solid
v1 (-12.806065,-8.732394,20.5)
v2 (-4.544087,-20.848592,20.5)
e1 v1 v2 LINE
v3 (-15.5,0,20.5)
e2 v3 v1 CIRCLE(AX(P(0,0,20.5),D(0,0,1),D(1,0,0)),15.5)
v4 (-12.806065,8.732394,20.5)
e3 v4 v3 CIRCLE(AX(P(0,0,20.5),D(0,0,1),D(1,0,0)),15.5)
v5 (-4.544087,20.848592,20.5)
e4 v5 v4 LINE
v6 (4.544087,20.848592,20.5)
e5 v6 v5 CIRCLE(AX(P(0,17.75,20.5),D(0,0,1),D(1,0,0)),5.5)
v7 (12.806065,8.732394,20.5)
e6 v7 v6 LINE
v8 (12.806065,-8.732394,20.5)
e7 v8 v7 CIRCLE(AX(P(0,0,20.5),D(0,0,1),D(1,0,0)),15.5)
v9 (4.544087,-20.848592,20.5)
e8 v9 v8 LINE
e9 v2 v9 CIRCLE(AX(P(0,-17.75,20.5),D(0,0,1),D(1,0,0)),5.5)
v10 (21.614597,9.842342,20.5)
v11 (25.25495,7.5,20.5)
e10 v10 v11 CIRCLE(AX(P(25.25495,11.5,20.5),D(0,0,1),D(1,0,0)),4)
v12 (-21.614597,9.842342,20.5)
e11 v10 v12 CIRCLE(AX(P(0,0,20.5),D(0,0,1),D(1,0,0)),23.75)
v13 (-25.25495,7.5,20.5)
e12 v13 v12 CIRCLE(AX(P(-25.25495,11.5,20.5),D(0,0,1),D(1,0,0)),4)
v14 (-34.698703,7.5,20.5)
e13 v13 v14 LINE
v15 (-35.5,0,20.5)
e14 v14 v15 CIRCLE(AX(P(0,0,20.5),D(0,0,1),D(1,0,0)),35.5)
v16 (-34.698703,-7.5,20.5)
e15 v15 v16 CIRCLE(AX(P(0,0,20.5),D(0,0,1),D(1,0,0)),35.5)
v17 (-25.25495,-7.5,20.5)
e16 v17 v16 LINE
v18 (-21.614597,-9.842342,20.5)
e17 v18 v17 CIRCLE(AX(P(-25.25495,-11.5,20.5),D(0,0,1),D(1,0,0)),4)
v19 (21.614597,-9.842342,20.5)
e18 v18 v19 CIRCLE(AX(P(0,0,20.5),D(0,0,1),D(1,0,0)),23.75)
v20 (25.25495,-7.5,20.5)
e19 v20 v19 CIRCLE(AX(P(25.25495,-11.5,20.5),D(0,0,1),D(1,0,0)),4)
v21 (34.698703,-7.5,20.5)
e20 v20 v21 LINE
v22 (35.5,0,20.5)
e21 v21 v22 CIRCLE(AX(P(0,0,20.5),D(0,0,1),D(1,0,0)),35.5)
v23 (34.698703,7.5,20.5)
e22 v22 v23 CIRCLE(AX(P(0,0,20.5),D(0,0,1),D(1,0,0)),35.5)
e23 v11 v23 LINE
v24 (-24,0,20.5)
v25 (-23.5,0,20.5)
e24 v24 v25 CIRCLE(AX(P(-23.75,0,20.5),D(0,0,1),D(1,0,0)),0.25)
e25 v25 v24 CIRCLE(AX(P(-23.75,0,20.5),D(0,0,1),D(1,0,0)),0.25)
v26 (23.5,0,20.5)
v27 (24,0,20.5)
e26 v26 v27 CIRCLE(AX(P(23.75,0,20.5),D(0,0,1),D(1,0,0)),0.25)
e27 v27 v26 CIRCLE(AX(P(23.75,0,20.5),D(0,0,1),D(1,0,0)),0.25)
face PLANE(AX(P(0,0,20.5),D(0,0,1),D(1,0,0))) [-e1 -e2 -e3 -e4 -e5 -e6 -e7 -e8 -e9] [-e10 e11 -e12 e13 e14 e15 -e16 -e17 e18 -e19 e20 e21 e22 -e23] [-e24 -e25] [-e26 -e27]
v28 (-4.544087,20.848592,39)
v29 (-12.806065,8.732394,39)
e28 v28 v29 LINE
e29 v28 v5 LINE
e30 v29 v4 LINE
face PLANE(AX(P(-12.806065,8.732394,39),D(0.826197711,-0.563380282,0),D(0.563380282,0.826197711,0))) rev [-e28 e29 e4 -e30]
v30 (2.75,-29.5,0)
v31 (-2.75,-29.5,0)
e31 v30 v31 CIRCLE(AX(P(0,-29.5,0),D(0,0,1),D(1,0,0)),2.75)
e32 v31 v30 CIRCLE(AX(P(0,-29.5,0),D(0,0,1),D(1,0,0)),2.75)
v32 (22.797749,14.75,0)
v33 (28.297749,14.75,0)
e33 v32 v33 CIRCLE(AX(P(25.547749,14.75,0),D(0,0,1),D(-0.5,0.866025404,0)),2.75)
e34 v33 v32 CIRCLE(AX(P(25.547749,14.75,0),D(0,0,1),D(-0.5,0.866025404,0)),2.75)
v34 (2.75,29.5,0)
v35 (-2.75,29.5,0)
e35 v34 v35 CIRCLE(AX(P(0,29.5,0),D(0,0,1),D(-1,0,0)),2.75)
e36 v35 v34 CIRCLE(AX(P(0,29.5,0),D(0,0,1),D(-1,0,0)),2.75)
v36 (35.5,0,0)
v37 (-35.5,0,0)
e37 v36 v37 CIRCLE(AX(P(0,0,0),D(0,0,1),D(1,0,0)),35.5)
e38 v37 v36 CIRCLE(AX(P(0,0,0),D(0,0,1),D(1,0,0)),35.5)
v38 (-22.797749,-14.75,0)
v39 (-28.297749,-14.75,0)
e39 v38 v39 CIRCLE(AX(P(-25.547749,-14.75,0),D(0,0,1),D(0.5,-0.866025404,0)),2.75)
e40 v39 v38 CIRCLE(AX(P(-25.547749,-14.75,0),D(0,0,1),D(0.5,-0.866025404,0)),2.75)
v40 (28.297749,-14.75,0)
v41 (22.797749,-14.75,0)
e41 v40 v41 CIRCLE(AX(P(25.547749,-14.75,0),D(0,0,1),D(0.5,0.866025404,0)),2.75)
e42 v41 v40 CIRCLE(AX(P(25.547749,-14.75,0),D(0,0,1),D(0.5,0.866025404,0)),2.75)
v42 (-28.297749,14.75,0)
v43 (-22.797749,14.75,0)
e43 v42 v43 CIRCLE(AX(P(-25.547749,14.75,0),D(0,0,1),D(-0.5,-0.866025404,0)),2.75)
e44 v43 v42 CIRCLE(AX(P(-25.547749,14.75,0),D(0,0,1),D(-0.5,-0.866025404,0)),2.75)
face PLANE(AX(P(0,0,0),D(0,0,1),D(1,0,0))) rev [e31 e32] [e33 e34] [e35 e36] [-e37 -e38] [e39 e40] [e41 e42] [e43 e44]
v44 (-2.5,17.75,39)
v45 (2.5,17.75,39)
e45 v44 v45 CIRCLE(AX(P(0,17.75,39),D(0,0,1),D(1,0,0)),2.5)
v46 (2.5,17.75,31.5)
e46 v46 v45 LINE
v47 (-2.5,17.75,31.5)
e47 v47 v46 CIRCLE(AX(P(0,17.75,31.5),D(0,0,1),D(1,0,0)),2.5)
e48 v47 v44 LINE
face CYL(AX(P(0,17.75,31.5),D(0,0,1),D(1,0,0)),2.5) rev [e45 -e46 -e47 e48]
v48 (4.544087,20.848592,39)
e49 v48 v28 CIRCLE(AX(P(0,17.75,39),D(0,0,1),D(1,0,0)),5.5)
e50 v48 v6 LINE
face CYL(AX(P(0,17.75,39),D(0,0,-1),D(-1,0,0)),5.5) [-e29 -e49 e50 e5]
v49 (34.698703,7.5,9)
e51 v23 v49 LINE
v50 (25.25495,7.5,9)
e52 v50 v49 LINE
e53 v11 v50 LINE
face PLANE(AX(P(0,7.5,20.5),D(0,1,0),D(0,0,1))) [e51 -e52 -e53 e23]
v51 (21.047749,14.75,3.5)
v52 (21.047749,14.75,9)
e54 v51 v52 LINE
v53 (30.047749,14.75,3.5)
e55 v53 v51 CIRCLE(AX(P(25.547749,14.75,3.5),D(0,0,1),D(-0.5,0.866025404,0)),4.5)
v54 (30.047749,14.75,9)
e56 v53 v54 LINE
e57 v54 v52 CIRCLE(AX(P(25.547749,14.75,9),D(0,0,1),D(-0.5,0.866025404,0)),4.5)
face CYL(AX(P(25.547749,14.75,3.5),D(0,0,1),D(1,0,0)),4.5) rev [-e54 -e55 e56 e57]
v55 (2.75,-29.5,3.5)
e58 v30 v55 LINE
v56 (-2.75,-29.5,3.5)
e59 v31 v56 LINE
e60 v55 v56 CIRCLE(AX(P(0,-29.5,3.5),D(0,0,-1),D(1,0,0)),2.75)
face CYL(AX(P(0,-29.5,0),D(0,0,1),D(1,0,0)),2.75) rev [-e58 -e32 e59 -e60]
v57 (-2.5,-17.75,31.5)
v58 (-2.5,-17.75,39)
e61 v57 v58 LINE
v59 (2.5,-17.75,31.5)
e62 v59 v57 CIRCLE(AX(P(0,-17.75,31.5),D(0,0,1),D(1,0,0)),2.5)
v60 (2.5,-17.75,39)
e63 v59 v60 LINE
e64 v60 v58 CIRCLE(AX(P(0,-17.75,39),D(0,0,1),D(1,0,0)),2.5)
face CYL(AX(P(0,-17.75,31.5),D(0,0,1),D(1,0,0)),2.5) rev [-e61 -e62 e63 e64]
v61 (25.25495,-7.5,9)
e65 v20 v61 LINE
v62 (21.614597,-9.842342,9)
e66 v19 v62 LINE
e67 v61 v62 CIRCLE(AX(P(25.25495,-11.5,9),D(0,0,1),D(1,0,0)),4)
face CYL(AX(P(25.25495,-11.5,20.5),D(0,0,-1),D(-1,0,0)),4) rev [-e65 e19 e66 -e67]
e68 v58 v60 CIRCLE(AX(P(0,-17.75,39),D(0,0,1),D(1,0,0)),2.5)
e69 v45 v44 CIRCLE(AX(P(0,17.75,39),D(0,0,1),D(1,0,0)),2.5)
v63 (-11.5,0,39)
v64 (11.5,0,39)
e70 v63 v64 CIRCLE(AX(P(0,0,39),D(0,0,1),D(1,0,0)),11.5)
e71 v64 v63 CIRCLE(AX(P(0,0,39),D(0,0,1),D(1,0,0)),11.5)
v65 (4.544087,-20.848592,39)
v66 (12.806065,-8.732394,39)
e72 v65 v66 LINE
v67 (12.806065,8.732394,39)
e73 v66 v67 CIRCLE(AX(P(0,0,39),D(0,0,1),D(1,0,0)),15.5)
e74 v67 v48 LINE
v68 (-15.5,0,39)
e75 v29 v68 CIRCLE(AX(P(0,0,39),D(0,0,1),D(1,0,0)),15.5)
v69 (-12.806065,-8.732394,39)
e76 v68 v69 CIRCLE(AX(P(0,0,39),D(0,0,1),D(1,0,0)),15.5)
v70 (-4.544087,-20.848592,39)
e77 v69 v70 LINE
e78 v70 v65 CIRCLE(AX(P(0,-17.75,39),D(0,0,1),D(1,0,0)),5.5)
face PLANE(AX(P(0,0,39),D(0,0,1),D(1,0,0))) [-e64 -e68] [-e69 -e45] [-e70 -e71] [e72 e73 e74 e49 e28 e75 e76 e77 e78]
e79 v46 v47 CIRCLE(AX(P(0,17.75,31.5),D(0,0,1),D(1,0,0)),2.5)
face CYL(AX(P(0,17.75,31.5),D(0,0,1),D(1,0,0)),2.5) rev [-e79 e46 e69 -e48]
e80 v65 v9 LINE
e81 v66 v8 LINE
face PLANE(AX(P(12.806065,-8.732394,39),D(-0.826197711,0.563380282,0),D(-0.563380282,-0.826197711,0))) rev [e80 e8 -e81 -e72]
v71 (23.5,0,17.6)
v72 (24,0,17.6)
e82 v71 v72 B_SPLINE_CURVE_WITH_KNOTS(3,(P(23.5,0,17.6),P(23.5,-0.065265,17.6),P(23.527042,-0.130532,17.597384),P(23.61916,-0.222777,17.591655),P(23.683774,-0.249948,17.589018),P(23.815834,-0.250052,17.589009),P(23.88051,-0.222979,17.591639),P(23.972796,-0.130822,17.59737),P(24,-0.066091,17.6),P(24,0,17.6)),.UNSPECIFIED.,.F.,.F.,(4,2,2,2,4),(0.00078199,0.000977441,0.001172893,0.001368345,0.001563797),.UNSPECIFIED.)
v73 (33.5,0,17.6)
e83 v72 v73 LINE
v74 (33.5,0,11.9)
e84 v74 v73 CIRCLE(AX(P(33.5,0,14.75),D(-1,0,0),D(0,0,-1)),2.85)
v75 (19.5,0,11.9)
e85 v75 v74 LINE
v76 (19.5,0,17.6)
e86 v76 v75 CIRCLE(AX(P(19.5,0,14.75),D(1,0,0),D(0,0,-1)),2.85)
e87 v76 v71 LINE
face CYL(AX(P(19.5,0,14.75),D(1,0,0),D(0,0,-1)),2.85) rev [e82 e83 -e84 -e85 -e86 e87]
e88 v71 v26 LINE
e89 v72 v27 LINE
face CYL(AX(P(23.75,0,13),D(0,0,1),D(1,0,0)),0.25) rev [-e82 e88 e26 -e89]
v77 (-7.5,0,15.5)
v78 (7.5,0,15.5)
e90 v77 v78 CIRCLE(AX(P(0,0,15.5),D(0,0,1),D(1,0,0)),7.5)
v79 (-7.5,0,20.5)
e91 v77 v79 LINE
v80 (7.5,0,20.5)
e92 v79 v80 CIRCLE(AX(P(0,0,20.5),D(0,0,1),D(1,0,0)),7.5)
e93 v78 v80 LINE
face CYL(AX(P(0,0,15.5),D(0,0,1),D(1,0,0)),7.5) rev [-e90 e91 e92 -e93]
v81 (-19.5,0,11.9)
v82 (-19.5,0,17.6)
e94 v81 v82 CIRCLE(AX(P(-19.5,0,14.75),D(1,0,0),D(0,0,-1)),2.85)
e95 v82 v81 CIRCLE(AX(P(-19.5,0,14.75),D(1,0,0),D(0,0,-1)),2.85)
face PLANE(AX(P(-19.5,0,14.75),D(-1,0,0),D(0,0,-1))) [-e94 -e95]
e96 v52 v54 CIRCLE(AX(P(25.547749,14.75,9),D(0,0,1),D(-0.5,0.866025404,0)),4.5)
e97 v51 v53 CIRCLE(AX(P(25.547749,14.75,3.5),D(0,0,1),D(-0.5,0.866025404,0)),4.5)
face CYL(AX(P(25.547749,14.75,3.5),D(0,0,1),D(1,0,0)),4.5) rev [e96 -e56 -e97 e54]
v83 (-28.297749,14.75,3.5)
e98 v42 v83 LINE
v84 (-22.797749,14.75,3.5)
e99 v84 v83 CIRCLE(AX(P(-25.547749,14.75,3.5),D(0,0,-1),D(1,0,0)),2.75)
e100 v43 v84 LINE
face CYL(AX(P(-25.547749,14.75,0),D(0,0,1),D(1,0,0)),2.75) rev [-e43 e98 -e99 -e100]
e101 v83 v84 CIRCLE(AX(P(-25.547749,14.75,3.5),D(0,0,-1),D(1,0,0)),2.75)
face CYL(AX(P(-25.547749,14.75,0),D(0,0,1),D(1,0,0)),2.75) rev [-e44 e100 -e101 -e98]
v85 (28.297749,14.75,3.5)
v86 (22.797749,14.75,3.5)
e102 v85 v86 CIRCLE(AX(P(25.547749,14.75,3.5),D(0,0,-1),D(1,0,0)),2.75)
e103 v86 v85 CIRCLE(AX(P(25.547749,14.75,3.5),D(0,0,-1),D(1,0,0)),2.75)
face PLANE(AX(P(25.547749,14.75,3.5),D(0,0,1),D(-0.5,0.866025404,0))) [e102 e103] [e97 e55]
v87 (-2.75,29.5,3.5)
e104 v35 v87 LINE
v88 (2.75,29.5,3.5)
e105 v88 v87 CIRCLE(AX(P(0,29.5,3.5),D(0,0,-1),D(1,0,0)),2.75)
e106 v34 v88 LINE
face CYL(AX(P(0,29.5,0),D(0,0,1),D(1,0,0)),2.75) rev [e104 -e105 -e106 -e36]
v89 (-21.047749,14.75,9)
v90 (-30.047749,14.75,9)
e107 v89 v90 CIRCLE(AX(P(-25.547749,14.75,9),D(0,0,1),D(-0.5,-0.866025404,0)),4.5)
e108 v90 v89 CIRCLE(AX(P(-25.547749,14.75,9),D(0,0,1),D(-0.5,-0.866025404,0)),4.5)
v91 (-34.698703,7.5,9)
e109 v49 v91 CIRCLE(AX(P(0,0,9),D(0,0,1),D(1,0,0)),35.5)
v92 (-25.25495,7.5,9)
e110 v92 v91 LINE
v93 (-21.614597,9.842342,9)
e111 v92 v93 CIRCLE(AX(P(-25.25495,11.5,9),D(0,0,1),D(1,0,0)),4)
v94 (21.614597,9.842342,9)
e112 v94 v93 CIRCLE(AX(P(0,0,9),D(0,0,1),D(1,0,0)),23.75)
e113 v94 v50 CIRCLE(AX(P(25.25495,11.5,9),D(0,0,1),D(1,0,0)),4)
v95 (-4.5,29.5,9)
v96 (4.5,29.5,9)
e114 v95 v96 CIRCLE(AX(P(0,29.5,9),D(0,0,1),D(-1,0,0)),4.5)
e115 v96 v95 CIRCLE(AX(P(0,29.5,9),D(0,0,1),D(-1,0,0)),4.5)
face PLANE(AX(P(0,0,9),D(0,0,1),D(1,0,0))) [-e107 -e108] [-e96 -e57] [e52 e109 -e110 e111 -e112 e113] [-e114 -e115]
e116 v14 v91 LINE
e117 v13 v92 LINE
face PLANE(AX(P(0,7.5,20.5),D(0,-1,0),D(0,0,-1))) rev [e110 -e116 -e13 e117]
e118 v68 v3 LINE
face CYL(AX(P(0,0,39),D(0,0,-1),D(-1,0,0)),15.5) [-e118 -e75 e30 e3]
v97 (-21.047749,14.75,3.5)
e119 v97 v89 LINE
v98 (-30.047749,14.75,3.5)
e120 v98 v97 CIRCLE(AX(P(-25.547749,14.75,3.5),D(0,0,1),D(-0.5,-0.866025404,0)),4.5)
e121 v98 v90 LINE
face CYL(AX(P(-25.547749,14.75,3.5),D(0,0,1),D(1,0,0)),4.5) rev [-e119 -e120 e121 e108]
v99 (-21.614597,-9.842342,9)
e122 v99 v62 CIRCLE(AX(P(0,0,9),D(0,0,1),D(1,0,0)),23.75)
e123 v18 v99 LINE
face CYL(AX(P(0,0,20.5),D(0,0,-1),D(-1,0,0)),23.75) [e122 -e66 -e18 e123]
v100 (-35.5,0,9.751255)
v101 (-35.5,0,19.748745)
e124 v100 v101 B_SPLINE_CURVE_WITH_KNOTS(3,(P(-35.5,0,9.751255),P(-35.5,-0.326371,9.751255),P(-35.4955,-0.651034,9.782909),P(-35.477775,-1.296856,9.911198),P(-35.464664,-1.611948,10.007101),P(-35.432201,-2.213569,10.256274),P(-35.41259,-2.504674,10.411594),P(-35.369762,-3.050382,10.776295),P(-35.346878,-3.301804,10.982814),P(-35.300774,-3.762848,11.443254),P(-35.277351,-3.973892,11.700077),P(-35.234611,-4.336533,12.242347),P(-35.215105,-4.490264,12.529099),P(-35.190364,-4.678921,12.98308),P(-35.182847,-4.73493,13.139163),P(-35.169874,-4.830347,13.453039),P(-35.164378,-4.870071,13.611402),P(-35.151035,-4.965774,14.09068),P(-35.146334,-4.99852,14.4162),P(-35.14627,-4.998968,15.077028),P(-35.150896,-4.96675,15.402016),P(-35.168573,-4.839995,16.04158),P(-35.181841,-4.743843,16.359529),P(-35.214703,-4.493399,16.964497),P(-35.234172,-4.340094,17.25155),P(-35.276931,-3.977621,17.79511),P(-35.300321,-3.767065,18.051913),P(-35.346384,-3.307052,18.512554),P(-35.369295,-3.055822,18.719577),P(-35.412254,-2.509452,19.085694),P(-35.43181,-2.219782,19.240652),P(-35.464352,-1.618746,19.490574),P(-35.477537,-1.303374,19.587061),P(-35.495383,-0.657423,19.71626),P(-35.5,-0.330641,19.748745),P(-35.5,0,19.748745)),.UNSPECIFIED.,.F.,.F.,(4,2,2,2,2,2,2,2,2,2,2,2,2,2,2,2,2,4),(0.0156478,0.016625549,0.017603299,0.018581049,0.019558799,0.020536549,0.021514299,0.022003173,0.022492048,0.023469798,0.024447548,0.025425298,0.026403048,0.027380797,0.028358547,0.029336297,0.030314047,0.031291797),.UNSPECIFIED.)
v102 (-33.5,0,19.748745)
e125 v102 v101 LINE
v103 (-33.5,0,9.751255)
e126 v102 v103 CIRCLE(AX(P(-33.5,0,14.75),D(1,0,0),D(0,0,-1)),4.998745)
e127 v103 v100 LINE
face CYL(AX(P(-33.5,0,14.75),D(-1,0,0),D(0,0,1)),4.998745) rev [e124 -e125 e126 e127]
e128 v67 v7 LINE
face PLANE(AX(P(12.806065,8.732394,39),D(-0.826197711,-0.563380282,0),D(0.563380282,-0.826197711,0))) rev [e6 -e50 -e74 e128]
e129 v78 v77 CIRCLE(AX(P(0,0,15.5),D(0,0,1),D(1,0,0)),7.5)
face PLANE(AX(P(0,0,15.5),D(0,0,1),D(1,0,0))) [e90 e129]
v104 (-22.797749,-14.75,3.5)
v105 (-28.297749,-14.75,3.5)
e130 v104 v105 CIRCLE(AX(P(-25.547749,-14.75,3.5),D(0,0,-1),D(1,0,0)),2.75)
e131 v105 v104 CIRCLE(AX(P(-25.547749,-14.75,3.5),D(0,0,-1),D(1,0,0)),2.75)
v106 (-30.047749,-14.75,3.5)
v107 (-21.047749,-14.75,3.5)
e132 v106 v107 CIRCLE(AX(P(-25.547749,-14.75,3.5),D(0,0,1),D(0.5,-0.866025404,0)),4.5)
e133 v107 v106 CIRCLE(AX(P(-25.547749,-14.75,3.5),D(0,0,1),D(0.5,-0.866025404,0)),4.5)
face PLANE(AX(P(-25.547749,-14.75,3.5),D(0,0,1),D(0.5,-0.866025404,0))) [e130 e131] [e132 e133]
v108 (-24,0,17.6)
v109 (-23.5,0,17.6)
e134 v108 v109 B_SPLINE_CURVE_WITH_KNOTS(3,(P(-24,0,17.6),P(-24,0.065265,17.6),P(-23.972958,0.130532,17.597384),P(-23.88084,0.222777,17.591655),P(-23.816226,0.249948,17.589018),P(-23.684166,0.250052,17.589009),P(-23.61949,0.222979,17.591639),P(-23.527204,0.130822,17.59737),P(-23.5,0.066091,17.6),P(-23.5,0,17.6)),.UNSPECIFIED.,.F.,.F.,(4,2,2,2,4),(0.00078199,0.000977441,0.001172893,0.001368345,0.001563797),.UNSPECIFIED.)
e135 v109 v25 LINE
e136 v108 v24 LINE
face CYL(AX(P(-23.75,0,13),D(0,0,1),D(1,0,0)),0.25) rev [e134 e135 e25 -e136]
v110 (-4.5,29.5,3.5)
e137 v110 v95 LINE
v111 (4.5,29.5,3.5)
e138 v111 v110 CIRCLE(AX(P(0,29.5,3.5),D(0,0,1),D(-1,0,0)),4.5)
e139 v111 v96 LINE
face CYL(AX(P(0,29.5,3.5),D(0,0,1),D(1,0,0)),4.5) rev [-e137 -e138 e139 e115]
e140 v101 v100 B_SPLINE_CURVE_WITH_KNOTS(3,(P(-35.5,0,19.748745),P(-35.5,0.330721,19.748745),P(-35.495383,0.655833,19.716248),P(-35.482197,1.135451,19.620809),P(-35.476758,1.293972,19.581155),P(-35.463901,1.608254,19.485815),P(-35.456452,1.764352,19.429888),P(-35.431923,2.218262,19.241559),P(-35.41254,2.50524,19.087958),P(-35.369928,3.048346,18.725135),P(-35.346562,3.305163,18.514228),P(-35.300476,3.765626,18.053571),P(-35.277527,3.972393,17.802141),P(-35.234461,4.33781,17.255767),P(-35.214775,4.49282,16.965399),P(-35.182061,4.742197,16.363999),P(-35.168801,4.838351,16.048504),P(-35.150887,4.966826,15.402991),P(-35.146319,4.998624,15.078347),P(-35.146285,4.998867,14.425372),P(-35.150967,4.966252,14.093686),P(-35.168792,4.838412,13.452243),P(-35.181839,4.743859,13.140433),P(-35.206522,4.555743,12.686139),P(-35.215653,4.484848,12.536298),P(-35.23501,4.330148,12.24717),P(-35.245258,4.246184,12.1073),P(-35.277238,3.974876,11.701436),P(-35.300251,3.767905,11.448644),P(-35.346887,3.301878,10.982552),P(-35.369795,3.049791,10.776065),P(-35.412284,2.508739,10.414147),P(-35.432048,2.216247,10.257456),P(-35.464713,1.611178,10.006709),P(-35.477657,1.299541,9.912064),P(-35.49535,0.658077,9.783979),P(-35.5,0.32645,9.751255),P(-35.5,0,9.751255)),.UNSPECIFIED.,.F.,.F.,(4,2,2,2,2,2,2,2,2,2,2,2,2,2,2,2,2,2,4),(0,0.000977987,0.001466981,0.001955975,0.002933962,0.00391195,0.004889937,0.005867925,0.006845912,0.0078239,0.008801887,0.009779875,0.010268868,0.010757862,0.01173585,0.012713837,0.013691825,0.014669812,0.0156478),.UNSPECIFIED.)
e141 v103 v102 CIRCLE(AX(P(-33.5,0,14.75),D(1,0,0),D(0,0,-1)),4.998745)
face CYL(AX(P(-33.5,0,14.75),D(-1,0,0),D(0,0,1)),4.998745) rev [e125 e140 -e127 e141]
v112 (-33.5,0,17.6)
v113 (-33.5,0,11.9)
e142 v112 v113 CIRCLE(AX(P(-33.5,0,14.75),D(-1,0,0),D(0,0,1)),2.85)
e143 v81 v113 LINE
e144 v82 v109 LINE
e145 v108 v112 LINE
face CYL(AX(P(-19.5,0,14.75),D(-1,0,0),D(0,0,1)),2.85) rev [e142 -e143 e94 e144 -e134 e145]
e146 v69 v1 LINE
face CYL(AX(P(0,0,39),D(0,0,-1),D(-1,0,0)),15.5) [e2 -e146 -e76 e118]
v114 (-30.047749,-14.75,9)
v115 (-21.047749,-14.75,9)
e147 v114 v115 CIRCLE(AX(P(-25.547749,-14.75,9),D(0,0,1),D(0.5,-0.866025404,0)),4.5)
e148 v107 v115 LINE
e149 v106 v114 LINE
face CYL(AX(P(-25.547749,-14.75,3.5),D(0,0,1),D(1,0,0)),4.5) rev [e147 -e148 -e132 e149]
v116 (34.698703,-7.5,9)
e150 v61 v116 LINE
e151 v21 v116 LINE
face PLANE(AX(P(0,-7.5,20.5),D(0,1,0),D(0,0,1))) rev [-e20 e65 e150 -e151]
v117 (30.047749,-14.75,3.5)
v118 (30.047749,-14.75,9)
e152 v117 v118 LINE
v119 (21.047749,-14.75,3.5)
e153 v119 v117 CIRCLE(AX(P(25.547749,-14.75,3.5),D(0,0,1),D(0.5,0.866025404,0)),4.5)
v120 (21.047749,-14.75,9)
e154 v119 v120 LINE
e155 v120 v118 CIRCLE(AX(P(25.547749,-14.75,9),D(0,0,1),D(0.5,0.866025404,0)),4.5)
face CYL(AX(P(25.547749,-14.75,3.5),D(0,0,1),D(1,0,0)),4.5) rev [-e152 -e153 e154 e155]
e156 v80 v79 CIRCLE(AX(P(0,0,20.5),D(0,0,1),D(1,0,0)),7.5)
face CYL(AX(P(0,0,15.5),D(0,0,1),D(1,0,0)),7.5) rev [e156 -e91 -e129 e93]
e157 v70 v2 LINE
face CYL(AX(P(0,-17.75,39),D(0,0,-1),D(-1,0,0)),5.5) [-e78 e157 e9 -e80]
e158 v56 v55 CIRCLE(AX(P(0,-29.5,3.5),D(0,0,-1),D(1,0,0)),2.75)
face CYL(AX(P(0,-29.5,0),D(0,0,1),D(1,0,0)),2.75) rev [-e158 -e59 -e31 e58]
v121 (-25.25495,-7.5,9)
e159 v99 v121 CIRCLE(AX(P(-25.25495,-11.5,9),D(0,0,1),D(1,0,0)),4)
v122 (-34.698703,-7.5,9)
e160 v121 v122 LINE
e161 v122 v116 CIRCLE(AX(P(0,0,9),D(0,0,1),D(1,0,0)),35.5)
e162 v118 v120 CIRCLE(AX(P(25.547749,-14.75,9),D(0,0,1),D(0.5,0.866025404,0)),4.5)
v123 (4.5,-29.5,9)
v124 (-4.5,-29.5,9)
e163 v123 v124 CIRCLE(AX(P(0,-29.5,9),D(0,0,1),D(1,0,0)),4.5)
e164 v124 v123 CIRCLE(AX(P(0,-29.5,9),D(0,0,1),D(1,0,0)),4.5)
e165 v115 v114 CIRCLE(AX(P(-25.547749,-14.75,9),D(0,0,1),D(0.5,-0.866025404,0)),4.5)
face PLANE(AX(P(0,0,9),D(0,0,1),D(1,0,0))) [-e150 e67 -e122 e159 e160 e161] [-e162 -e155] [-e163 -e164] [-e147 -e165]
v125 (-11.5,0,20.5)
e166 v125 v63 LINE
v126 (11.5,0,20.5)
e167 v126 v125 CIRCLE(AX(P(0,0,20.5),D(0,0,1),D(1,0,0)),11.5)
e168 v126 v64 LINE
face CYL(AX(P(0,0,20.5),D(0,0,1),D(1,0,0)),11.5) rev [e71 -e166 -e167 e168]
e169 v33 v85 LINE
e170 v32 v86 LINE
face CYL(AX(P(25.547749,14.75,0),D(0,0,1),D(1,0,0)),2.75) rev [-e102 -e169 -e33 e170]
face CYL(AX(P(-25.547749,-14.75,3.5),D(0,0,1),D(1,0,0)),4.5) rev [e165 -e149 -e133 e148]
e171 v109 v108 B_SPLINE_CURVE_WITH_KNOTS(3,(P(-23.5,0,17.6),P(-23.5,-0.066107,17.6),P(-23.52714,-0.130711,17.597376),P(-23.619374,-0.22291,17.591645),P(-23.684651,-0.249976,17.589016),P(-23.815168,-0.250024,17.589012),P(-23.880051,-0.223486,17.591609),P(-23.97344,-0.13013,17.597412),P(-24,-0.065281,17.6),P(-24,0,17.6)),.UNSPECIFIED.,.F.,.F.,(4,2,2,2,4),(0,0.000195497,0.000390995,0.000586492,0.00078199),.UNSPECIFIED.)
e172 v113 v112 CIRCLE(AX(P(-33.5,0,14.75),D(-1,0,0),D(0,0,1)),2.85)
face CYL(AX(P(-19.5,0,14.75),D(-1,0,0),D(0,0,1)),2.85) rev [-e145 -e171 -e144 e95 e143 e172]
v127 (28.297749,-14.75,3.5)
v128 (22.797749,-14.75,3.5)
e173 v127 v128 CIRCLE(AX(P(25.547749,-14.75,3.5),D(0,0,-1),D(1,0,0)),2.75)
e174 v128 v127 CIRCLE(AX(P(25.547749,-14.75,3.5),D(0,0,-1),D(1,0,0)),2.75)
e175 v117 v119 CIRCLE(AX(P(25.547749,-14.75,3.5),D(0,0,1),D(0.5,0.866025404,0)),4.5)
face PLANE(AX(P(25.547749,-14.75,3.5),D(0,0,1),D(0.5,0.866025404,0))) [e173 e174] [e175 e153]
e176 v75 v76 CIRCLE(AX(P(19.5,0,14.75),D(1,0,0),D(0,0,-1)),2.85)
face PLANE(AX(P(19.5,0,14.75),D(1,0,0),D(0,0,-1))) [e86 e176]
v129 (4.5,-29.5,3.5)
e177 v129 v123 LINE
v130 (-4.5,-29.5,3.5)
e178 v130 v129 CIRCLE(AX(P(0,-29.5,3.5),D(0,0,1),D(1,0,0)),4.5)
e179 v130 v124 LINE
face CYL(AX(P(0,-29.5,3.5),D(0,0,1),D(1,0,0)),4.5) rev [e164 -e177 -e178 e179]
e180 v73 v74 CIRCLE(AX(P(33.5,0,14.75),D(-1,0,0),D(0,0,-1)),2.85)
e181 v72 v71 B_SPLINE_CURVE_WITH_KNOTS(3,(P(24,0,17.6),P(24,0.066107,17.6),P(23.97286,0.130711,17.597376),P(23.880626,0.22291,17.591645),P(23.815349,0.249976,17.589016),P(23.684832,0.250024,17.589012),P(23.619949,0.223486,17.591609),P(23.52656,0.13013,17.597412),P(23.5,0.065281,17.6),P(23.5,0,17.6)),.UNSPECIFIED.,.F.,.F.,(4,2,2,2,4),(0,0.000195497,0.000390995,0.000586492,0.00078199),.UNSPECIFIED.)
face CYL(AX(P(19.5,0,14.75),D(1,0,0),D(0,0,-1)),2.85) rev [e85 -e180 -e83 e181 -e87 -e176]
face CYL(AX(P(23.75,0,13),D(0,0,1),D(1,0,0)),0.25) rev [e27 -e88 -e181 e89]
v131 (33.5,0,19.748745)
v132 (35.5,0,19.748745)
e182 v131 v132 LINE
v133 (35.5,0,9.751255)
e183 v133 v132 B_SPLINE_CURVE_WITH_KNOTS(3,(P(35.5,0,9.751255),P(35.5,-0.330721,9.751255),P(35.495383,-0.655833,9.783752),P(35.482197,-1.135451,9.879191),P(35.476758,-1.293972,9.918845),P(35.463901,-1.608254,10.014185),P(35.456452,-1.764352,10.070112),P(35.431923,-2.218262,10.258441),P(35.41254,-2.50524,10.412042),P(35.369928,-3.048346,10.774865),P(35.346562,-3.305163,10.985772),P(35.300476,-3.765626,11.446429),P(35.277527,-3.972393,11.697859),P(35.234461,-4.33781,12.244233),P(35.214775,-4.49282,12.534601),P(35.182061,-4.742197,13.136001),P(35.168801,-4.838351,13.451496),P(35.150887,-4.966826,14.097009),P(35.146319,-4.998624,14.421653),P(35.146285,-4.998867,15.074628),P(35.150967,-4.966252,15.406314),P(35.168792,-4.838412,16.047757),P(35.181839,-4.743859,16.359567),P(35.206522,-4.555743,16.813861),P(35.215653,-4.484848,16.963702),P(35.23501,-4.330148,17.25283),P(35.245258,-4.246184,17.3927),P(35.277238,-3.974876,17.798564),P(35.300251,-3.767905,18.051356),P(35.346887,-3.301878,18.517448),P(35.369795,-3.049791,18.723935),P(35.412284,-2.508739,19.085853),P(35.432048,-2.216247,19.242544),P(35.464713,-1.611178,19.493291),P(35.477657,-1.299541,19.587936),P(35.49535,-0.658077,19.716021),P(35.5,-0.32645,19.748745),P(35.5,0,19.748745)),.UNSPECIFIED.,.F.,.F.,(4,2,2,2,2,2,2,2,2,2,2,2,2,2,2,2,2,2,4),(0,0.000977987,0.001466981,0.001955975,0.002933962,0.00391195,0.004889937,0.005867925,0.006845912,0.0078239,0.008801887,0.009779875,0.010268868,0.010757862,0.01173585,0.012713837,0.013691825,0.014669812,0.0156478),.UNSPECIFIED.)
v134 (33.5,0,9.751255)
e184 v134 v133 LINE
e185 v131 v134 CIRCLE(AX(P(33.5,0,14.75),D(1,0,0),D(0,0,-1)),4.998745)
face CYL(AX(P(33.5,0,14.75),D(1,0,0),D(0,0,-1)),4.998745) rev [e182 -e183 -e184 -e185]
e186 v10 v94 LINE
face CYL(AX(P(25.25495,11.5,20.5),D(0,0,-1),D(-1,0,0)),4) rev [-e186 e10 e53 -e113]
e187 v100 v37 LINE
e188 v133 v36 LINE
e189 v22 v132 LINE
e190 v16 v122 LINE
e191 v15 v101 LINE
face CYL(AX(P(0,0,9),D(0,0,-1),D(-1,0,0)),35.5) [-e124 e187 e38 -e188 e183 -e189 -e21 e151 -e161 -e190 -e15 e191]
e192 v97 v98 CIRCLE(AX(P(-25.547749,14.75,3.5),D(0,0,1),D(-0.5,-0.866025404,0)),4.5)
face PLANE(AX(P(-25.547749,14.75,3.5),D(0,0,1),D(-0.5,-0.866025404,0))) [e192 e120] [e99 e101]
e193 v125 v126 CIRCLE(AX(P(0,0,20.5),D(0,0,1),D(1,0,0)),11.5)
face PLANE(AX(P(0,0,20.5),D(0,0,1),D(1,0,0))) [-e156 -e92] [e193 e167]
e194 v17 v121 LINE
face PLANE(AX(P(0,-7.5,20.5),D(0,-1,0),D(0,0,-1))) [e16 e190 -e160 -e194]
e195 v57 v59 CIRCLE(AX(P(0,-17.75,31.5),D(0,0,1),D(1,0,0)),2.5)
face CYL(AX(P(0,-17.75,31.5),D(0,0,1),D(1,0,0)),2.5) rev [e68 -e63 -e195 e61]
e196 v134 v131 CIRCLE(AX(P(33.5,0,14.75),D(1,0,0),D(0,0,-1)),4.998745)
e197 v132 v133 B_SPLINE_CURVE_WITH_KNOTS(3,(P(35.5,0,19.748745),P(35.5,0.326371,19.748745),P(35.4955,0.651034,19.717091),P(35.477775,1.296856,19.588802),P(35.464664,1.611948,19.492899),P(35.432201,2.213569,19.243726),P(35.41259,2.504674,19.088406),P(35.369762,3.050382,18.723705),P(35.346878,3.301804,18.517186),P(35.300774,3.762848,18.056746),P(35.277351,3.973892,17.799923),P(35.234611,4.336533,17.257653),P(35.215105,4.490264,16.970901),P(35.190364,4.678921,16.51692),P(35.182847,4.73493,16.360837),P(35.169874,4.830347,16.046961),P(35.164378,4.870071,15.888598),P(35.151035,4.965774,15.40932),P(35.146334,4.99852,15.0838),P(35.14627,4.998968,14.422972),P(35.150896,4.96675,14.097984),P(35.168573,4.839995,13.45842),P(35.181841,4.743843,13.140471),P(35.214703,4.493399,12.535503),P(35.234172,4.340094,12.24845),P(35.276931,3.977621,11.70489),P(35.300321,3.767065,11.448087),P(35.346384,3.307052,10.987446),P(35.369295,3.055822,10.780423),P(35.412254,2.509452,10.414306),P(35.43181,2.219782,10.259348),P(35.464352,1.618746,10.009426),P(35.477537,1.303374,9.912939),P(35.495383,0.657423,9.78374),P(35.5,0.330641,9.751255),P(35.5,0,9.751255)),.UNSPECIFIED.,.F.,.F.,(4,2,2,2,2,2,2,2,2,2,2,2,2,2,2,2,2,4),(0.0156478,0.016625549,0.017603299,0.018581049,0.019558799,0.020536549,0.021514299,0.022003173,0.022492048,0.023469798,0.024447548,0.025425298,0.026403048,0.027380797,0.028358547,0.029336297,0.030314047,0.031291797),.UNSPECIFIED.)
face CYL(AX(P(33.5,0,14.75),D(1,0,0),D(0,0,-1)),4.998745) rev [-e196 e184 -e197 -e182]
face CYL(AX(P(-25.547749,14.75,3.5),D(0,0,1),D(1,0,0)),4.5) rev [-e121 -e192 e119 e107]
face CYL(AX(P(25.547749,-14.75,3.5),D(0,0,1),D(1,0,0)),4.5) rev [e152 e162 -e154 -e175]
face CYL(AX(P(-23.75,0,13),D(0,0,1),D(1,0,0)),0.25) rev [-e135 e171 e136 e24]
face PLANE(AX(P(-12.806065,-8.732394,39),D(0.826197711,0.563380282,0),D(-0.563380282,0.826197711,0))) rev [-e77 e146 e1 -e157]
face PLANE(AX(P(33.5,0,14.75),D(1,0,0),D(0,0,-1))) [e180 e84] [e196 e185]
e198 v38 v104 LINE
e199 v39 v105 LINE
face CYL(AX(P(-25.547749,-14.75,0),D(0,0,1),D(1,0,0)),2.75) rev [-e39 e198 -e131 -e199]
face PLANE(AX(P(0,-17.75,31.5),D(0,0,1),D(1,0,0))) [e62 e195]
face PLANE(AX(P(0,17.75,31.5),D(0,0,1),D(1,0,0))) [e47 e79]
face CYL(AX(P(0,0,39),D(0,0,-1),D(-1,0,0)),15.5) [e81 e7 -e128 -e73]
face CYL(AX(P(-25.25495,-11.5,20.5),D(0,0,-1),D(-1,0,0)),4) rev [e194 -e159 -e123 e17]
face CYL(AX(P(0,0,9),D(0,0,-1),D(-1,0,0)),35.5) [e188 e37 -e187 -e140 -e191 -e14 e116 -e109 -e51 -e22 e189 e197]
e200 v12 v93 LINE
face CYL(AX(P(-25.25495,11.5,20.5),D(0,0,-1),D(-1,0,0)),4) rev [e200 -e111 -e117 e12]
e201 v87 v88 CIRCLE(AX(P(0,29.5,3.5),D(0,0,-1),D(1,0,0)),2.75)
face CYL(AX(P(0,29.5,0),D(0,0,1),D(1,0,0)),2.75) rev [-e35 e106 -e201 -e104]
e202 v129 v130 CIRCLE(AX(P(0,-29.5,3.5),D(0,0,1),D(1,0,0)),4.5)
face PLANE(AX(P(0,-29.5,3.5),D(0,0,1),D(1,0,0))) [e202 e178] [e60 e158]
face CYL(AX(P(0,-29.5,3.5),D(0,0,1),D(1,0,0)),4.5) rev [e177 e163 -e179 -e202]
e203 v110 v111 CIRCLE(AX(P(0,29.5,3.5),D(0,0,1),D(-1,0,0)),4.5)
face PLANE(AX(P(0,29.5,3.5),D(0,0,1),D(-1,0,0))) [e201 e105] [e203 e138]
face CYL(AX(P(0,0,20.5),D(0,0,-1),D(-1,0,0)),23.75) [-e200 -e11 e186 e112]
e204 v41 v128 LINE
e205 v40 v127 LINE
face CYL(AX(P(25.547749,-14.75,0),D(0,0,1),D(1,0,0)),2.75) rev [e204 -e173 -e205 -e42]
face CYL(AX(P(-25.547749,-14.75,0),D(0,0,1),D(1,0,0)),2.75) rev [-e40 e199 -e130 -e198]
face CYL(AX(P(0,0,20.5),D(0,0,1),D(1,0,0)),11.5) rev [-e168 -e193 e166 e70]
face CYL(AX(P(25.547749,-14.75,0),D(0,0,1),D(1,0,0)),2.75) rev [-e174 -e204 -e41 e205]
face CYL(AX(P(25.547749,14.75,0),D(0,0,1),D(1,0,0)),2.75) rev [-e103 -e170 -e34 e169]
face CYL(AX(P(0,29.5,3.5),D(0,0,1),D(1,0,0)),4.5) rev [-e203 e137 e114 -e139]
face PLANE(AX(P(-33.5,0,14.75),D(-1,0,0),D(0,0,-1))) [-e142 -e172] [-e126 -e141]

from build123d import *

# Parameters (mm, degrees)
FLANGE_DISC_SKETCH_R             = 35.5
FLANGE_DISC_71X9_DEPTH           = 9
MOUNTING_LUG_PLATE_DEPTH         = 11.5
HUB_BOSS_DEPTH                   = 18.5
RADIAL_PORT_HOLE_SKETCH_R        = 2.85
RADIAL_PORT_HOLE_5_7_DEPTH       = 16
RADIAL_PORT_COUNTERBORE_SKETCH_R = 4.99874543
RADIAL_PORT_COUNTERBORE_10_DEPTH = 2
MAIN_BORE_SKETCH_R               = 11.5
MAIN_BORE_23_DEPTH               = 18.5
THROUGH_BORE_SKETCH_R            = 7.5
THROUGH_BORE_15_DEPTH            = 5
BOLT_HOLE_SKETCH_R               = 2.75
BOLT_HOLE_5_5_DEPTH              = 59.485040944
BOLT_HOLE_COUNTERBORE_SKETCH_R   = 4.5
BOLT_HOLE_COUNTERBORE_9_DEPTH    = 5.5
BOLT_HOLE_PATTERN_6X_COUNT       = 6
LUG_HOLES_SKETCH_R               = 2.5
LUG_HOLES_5_DEPTH                = 7.5
RELIEF_GROOVE_SKETCH_R           = 0.25
RELIEF_GROOVE_DEPTH              = 7.5


with BuildPart() as part:
    # Flange Disc Sketch → Flange Disc Ø71x9 (new body)
    with BuildSketch(Plane.XY):
        Circle(FLANGE_DISC_SKETCH_R)
    extrude(amount=FLANGE_DISC_71X9_DEPTH)

    # Mounting Lug Plate Sketch → Mounting Lug Plate (add)
    with BuildSketch(Plane.XY.offset(9)):
        with BuildLine():
            ThreePointArc((-21.614596855, 9.842342342), (-23.090536767, 8.136175493), (-25.25495001, 7.5))
            Line((-25.25495001, 7.5), (-34.698703146, 7.5))
            ThreePointArc((-34.698703146, 7.5), (-35.5, 0), (-34.698703146, -7.5))
            Line((-34.698703146, -7.5), (-25.25495001, -7.5))
            ThreePointArc((-25.25495001, -7.5), (-23.090536767, -8.136175493), (-21.614596855, -9.842342342))
            ThreePointArc((-21.614596855, -9.842342342), (0, -23.75), (21.614596855, -9.842342342))
            ThreePointArc((21.614596855, -9.842342342), (23.090536767, -8.136175493), (25.25495001, -7.5))
            Line((25.25495001, -7.5), (34.698703146, -7.5))
            ThreePointArc((34.698703146, -7.5), (35.299107366, -3.771341825), (35.5, 0))
            ThreePointArc((35.5, 0), (35.299107366, 3.771341825), (34.698703146, 7.5))
            Line((34.698703146, 7.5), (25.25495001, 7.5))
            ThreePointArc((25.25495001, 7.5), (23.090536767, 8.136175493), (21.614596855, 9.842342342))
            ThreePointArc((21.614596855, 9.842342342), (0, 23.75), (-21.614596855, 9.842342342))
        make_face()
    extrude(amount=MOUNTING_LUG_PLATE_DEPTH)

    # Hub Profile Sketch → Hub Boss (add)
    with BuildSketch(Plane.XY.offset(20.5)):
        with BuildLine():
            Line((-12.806064526, 8.732394366), (-4.544087412, 20.848591549))
            ThreePointArc((-4.544087412, 20.848591549), (0, 23.25), (4.544087412, 20.848591549))
            Line((4.544087412, 20.848591549), (12.806064526, 8.732394366))
            ThreePointArc((12.806064526, 8.732394366), (15.5, 0), (12.806064526, -8.732394366))
            Line((12.806064526, -8.732394366), (4.544087412, -20.848591549))
            ThreePointArc((4.544087412, -20.848591549), (0, -23.25), (-4.544087412, -20.848591549))
            Line((-4.544087412, -20.848591549), (-12.806064526, -8.732394366))
            ThreePointArc((-12.806064526, -8.732394366), (-15.5, 0), (-12.806064526, 8.732394366))
        make_face()
    extrude(amount=HUB_BOSS_DEPTH)

    # Radial Port Hole Sketch → Radial Port Hole Ø5.7 (cut)
    with BuildSketch(Plane(origin=(35.5, 0, 0), x_dir=(0, 0, -1), z_dir=(1, 0, 0))):
        with Locations((-14.75, 0)):
            Circle(RADIAL_PORT_HOLE_SKETCH_R)
    radial_port_hole_5_7 = extrude(amount=-RADIAL_PORT_HOLE_5_7_DEPTH, mode=Mode.SUBTRACT)

    # Radial Port Counterbore Sketch → Radial Port Counterbore Ø10 (cut)
    with BuildSketch(Plane(origin=(35.5, 0, 0), x_dir=(0, 0, -1), z_dir=(1, 0, 0))):
        with Locations((-14.75, 0)):
            Circle(RADIAL_PORT_COUNTERBORE_SKETCH_R)
    radial_port_counterbore_10 = extrude(amount=-RADIAL_PORT_COUNTERBORE_10_DEPTH, mode=Mode.SUBTRACT)

    # Radial Port Mirror: Radial Port Hole Ø5.7, Radial Port Counterbore Ø10 across plane
    add(radial_port_hole_5_7.mirror(Plane(origin=(0, 0, 0), x_dir=(0, 0, 1), z_dir=(1, 0, 0))), mode=Mode.SUBTRACT)
    add(radial_port_counterbore_10.mirror(Plane(origin=(0, 0, 0), x_dir=(0, 0, 1), z_dir=(1, 0, 0))), mode=Mode.SUBTRACT)

    # Main Bore Sketch → Main Bore Ø23 (cut)
    with BuildSketch(Plane.XY.offset(39)):
        Circle(MAIN_BORE_SKETCH_R)
    extrude(amount=-MAIN_BORE_23_DEPTH, mode=Mode.SUBTRACT)

    # Through Bore Sketch → Through Bore Ø15 (cut)
    with BuildSketch(Plane.XY.offset(20.5)):
        Circle(THROUGH_BORE_SKETCH_R)
    extrude(amount=-THROUGH_BORE_15_DEPTH, mode=Mode.SUBTRACT)

    # Bolt Hole Sketch → Bolt Hole Ø5.5 (cut, through all)
    with BuildSketch(Plane.XY.offset(9)):
        with Locations((0, -29.5)):
            Circle(BOLT_HOLE_SKETCH_R)
    bolt_hole_5_5 = extrude(amount=-BOLT_HOLE_5_5_DEPTH, mode=Mode.SUBTRACT)

    # Bolt Hole Counterbore Sketch → Bolt Hole Counterbore Ø9 (cut)
    with BuildSketch(Plane.XY.offset(9)):
        with Locations((0, -29.5)):
            Circle(BOLT_HOLE_COUNTERBORE_SKETCH_R)
    bolt_hole_counterbore_9 = extrude(amount=-BOLT_HOLE_COUNTERBORE_9_DEPTH, mode=Mode.SUBTRACT)

    # Bolt Hole Pattern 6x: Bolt Hole Ø5.5, Bolt Hole Counterbore Ø9 ×6 about axis
    bolt_hole_pattern_6x_axis = Axis((0, 0, 0), (0, 0, 1))
    add([bolt_hole_5_5.rotate(bolt_hole_pattern_6x_axis, i * 360 / BOLT_HOLE_PATTERN_6X_COUNT) for i in range(1, BOLT_HOLE_PATTERN_6X_COUNT)], mode=Mode.SUBTRACT)
    add([bolt_hole_counterbore_9.rotate(bolt_hole_pattern_6x_axis, i * 360 / BOLT_HOLE_PATTERN_6X_COUNT) for i in range(1, BOLT_HOLE_PATTERN_6X_COUNT)], mode=Mode.SUBTRACT)

    # Lug Holes Sketch → Lug Holes Ø5 (cut)
    with BuildSketch(Plane.XY.offset(39)):
        with Locations((0, 17.75)):
            Circle(LUG_HOLES_SKETCH_R)
        with Locations((0, -17.75)):
            Circle(LUG_HOLES_SKETCH_R)
    extrude(amount=-LUG_HOLES_5_DEPTH, mode=Mode.SUBTRACT)

    # Relief Groove Sketch → Relief Groove (cut)
    with BuildSketch(Plane.XY.offset(20.5)):
        with Locations((-23.75, 0)):
            Circle(RELIEF_GROOVE_SKETCH_R)
        with Locations((23.75, 0)):
            Circle(RELIEF_GROOVE_SKETCH_R)
    extrude(amount=-RELIEF_GROOVE_DEPTH, mode=Mode.SUBTRACT)


solid = part.part
